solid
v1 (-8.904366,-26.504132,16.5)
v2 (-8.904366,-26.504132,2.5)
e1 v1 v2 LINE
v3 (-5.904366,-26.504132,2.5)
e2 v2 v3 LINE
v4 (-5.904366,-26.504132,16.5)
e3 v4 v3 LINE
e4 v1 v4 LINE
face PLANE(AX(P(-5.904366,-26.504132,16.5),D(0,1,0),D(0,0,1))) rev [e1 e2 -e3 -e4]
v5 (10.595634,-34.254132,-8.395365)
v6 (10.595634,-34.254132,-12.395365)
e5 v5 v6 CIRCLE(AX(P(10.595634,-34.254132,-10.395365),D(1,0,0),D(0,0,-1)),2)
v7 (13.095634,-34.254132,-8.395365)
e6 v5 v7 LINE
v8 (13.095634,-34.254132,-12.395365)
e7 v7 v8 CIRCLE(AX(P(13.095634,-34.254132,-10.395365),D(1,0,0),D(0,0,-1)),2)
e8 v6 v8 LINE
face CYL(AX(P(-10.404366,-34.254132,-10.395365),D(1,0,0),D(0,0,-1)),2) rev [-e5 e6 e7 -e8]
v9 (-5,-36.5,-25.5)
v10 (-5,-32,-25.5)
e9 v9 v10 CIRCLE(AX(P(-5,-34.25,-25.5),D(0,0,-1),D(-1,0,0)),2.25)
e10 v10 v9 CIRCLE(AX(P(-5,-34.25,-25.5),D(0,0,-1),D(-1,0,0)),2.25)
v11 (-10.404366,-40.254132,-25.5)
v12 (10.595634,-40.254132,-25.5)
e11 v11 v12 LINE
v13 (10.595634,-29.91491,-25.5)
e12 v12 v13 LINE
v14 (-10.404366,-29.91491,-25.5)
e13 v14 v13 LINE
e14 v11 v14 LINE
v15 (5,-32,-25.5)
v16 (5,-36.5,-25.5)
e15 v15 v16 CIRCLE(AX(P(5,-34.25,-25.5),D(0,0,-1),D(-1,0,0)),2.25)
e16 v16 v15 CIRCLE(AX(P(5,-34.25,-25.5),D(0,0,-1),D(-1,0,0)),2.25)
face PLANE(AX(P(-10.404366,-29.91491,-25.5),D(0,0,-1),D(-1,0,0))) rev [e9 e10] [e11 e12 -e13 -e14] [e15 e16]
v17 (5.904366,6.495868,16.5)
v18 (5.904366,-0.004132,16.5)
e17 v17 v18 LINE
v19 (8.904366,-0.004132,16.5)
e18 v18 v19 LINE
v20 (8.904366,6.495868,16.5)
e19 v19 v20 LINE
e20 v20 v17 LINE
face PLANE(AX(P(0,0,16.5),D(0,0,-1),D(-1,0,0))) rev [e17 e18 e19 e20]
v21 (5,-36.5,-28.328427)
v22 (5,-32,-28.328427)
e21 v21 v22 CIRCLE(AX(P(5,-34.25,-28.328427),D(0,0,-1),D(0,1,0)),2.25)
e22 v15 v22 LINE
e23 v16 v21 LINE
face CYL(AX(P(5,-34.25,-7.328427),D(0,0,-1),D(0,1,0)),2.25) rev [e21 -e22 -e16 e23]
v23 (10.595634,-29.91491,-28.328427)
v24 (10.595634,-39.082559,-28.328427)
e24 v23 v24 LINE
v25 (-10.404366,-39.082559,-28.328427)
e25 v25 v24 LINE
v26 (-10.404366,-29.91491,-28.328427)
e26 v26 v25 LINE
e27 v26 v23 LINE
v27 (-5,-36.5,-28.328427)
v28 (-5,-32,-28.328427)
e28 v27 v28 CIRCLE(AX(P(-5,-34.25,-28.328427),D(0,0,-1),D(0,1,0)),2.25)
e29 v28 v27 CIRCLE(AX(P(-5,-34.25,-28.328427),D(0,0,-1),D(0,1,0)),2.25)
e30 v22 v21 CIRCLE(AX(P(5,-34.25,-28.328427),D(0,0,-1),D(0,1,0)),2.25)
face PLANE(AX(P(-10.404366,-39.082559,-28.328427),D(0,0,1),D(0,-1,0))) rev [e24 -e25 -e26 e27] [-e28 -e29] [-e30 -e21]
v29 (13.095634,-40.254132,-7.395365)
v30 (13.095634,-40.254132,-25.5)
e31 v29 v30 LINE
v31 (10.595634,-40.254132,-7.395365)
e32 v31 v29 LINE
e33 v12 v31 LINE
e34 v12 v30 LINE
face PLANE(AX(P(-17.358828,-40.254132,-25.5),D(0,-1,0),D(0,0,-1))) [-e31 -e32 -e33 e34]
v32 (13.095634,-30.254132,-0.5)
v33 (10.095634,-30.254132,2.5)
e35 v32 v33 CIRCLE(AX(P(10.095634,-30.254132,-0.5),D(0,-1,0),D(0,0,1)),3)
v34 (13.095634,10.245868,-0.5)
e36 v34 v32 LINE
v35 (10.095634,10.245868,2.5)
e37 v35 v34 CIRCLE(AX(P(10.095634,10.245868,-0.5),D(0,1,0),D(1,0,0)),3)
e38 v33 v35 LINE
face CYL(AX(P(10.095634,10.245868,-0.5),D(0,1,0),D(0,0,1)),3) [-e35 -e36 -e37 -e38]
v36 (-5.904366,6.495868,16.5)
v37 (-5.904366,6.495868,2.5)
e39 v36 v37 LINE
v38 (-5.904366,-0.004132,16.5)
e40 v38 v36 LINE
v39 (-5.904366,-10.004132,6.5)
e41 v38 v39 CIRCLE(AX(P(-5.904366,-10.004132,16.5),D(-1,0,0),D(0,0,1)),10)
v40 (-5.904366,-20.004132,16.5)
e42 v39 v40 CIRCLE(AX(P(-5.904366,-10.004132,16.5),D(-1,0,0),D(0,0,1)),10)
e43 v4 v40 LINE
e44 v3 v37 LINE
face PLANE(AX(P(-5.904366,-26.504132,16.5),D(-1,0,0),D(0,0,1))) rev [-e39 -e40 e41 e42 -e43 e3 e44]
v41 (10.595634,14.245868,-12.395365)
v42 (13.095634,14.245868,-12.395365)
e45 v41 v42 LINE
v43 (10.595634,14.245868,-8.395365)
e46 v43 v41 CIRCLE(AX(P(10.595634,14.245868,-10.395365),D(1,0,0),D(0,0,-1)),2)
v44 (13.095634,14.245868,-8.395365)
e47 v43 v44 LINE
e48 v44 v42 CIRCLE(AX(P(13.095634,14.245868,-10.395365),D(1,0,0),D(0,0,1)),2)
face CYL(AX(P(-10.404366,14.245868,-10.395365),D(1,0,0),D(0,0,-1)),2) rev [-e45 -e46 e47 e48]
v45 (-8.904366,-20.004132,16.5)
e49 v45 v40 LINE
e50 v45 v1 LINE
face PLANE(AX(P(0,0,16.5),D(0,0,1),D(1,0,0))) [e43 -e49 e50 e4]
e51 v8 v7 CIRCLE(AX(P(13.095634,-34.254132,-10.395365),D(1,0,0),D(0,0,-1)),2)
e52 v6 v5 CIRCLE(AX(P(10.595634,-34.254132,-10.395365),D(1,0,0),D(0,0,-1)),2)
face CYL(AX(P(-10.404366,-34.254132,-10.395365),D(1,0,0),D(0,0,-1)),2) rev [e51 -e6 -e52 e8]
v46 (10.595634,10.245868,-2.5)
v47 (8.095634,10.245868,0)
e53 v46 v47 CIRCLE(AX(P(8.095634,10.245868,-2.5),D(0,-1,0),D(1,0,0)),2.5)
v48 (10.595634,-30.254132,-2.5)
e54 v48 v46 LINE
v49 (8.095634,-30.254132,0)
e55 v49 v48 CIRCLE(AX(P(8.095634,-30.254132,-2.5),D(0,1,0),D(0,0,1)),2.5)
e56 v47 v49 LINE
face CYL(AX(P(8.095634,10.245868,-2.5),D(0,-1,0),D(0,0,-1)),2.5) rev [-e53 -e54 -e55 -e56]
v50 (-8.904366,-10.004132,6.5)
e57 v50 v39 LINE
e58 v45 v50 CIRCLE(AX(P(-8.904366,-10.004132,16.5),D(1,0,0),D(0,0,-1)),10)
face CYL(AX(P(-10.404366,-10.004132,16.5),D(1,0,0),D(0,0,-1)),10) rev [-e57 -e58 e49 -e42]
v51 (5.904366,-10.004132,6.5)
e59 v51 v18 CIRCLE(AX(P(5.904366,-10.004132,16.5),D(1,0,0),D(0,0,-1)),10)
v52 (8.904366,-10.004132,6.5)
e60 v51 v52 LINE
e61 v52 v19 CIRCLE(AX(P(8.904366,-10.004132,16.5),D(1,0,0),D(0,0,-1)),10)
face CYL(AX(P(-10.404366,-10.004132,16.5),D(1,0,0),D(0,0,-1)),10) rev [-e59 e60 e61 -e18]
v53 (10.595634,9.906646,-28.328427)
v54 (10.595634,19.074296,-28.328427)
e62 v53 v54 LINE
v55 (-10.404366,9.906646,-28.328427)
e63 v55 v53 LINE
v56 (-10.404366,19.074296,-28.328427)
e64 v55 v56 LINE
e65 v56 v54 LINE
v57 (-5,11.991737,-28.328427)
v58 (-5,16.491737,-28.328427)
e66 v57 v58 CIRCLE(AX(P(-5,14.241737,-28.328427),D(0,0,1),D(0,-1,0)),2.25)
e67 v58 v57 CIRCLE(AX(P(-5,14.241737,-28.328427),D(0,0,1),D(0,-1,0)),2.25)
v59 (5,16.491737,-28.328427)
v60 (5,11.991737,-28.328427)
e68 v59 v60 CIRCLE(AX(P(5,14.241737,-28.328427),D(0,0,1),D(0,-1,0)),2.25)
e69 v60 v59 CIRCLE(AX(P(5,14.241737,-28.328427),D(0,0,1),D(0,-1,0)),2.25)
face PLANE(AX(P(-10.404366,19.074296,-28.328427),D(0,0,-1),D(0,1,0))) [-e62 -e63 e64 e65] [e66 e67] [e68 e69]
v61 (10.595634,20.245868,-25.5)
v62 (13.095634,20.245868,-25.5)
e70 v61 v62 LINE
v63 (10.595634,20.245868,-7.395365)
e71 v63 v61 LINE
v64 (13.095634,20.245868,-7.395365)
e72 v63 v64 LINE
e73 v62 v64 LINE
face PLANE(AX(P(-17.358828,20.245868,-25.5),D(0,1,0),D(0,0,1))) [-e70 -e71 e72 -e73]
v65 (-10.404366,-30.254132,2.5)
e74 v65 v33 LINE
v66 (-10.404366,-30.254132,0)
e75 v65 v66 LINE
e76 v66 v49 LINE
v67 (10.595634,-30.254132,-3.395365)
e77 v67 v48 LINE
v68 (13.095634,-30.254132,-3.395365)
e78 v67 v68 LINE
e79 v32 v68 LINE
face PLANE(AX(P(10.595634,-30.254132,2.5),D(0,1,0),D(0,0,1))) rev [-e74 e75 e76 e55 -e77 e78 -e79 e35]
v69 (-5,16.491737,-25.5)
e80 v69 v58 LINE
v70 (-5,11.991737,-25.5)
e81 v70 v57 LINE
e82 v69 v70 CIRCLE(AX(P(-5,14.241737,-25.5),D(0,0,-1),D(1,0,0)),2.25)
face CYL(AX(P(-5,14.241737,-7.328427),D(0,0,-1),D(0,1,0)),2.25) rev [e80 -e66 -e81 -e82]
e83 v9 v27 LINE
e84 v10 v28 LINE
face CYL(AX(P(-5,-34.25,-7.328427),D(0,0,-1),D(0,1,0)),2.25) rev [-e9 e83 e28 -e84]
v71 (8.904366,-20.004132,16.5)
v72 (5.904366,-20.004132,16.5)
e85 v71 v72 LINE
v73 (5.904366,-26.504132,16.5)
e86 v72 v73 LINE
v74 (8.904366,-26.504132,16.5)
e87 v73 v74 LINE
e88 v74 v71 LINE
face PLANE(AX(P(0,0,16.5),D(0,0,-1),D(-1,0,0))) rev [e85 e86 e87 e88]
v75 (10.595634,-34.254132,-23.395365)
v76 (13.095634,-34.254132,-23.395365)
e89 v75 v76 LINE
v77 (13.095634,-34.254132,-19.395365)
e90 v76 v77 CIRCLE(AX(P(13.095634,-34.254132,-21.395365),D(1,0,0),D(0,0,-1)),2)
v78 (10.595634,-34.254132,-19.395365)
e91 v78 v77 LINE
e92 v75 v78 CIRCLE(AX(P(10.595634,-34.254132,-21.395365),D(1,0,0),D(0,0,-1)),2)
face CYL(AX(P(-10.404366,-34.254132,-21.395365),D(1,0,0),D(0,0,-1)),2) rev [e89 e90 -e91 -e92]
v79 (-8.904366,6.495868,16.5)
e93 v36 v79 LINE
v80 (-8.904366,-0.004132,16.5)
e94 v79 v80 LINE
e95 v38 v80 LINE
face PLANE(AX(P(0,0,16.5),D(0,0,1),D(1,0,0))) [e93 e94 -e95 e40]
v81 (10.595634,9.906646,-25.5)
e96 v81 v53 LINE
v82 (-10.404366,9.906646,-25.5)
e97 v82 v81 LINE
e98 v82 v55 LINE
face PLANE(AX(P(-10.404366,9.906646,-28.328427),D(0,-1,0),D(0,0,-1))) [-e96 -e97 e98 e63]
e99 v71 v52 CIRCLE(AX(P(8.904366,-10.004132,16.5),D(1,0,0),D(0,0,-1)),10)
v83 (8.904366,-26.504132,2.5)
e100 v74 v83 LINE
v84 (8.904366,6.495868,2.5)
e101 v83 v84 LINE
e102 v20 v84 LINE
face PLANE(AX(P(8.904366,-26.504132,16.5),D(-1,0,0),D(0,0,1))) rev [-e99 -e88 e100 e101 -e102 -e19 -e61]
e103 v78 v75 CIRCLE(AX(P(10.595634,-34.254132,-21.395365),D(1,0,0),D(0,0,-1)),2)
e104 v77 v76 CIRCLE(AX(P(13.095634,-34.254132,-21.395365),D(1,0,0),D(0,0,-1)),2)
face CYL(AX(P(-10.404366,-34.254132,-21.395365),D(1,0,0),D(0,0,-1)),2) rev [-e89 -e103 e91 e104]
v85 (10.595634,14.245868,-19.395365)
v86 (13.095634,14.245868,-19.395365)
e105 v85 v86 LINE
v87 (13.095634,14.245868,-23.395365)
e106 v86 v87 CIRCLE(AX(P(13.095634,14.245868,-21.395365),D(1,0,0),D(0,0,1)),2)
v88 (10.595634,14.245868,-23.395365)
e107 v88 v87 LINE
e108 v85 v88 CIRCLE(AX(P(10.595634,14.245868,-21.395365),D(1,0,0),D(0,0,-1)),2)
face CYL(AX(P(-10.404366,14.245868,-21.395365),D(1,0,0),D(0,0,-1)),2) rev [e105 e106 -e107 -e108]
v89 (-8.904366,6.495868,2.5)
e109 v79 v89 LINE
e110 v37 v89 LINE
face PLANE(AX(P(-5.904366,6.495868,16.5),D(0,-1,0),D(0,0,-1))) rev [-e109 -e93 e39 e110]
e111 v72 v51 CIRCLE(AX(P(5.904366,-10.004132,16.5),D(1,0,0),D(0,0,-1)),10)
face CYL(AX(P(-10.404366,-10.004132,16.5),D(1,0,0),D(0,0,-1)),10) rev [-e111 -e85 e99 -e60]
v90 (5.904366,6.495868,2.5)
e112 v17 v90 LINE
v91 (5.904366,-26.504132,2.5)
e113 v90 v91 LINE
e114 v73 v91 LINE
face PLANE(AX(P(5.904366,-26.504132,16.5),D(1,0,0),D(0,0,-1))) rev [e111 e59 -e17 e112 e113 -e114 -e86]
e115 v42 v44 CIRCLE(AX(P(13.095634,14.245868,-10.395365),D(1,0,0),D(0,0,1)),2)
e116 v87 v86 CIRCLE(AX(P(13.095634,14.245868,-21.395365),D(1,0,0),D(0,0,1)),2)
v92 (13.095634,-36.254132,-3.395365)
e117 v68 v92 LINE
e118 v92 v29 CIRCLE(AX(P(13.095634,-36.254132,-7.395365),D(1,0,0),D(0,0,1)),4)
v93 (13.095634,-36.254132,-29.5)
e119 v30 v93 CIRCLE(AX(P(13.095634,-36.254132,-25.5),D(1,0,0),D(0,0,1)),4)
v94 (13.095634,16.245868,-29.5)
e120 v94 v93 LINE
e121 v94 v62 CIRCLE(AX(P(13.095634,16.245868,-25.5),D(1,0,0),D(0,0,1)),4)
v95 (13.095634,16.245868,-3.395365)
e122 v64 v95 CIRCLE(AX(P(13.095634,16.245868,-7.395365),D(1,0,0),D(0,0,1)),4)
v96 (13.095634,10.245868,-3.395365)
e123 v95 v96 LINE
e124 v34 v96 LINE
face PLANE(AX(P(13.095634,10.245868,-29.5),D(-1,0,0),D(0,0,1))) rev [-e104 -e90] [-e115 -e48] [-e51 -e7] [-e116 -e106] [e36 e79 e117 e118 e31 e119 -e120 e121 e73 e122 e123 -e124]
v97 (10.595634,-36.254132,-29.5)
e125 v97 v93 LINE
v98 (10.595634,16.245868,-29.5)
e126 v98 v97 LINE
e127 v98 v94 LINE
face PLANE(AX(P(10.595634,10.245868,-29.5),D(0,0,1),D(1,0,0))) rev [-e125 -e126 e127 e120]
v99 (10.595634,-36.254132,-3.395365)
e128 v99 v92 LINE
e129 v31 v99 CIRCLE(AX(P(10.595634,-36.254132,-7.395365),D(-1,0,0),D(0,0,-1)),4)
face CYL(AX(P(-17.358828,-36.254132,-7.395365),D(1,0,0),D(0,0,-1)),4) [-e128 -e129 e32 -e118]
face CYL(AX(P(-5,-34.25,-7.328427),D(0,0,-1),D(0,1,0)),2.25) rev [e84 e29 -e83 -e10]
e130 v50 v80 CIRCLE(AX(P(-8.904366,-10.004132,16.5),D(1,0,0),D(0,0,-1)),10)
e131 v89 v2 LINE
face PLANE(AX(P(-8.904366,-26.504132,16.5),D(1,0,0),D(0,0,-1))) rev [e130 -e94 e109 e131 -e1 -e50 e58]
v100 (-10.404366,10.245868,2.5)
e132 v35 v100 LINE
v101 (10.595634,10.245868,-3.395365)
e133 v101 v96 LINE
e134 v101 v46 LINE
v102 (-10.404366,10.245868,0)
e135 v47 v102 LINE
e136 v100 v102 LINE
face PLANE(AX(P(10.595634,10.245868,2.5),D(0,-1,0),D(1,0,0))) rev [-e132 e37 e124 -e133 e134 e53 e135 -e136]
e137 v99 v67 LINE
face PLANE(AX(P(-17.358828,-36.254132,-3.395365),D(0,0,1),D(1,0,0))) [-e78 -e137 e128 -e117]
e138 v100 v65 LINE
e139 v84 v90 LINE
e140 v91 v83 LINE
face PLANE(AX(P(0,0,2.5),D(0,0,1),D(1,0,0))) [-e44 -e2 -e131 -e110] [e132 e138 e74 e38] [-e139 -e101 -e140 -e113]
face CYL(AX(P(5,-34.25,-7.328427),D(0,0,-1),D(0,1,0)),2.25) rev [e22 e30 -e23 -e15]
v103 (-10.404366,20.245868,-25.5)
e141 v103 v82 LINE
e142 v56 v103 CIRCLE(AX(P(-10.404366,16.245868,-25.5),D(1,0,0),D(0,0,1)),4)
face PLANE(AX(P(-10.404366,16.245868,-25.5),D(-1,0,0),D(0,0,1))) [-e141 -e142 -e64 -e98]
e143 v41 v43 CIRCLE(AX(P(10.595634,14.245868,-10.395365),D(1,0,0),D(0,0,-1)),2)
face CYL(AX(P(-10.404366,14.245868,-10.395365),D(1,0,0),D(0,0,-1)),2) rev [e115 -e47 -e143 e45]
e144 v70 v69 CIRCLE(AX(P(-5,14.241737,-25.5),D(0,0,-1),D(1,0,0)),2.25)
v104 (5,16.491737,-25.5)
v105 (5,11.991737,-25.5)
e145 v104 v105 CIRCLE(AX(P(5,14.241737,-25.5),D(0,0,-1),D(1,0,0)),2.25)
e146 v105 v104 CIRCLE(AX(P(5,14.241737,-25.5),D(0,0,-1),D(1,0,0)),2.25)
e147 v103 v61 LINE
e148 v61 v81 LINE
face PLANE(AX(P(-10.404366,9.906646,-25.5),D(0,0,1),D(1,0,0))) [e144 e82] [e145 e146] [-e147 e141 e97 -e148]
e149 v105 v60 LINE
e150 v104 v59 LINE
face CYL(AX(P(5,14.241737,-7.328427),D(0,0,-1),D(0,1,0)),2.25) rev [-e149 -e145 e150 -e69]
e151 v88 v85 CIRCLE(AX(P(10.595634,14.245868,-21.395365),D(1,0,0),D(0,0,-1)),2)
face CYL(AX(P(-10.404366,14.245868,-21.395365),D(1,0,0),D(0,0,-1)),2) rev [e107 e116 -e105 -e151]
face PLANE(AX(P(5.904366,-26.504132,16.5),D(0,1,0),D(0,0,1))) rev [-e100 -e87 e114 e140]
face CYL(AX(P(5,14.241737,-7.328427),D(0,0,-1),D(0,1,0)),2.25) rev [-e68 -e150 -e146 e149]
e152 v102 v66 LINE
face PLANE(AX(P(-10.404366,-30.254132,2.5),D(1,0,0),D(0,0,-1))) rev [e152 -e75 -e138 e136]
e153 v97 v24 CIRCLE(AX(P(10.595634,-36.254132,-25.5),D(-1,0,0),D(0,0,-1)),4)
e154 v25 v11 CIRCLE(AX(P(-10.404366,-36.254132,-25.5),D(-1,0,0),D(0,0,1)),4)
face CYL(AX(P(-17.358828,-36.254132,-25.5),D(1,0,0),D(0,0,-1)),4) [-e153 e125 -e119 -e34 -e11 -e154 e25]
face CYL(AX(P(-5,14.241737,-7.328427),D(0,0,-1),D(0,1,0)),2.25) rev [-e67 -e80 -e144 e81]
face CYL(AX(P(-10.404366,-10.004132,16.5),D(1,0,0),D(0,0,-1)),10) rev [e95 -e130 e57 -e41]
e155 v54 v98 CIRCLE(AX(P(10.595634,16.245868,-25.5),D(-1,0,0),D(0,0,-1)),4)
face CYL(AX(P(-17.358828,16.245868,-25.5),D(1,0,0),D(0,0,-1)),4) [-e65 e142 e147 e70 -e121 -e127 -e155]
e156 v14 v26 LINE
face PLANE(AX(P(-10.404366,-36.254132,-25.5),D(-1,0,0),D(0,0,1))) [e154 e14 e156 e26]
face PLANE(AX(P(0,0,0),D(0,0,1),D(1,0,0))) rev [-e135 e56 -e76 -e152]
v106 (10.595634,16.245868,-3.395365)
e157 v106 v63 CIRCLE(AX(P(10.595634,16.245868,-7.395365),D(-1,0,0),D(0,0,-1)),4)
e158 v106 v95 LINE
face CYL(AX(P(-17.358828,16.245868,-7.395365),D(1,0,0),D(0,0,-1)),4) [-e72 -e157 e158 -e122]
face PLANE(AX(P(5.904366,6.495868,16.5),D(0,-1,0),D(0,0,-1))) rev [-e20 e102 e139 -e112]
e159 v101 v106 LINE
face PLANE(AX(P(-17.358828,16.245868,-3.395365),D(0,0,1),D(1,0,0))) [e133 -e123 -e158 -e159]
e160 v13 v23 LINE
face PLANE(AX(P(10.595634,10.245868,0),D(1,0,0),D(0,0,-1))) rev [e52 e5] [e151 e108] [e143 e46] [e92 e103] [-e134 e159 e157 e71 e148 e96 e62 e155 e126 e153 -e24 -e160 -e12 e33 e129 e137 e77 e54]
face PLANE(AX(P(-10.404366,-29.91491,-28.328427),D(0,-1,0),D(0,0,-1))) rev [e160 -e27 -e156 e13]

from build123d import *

# Parameters (mm, degrees)
SKETCH2_W           = 21
SKETCH2_H           = 40.5
BOSS_EXTRUDE1_DEPTH = 2.5
SKETCH3_W           = 3
SKETCH3_H           = 33
BOSS_EXTRUDE2_DEPTH = 14
SKETCH4_R           = 10
CUT_EXTRUDE1_DEPTH  = 40.501767279
BOSS_EXTRUDE3_DEPTH = 20.25
FILLET1_R           = 3
FILLET2_R           = 2.5
BOSS_EXTRUDE4_DEPTH = 2.5
SKETCH7_R           = 2
CUT_EXTRUDE2_DEPTH  = 56.162442887
BOSS_EXTRUDE5_DEPTH = 21
SKETCH10_R          = 2.25
CUT_EXTRUDE3_DEPTH  = 21


with BuildPart() as part:
    # Sketch2 → Boss-Extrude1 (new body)
    with BuildSketch(Plane.XY):
        with Locations((0.095633845, -10.004131531)):
            Rectangle(SKETCH2_W, SKETCH2_H)
    extrude(amount=BOSS_EXTRUDE1_DEPTH)

    # Sketch3 → Boss-Extrude2 (add)
    with BuildSketch(Plane.XY.offset(2.5)):
        with Locations((-7.404366155, -10.004131531)):
            Rectangle(SKETCH3_W, SKETCH3_H)
        with Locations((7.404366155, -10.004131531)):
            Rectangle(SKETCH3_W, SKETCH3_H)
    extrude(amount=BOSS_EXTRUDE2_DEPTH)

    # Sketch4 → Cut-Extrude1 (cut, through all)
    with BuildSketch(Plane(origin=(8.904366155, 0, 0), x_dir=(0, 0, -1), z_dir=(1, 0, 0))):
        with Locations((-16.5, -10.004131531)):
            Circle(SKETCH4_R)
    extrude(amount=-CUT_EXTRUDE1_DEPTH, mode=Mode.SUBTRACT)

    # Sketch5 → Boss-Extrude3 (add, symmetric)
    with BuildSketch(Plane(origin=(0, -10.004131531, 0), x_dir=(1, 0, 0), z_dir=(0, 1, 0))):
        Polygon((10.595633845, 0), (10.595633845, 29.5), (13.095633845, 29.5), (13.095633845, -2.5), (10.595633845, -2.5), align=None)
    extrude(amount=BOSS_EXTRUDE3_DEPTH, both=True)

    # Fillet1
    fillet1_edges = [part.edges().sort_by_distance(p)[0] for p in [
        (13.095633845, -10.004131531, 2.5),
    ]]
    fillet(fillet1_edges, radius=FILLET1_R)

    # Fillet2
    fillet2_edges = [part.edges().sort_by_distance(p)[0] for p in [
        (10.595633845, -10.004131531, 0),
    ]]
    fillet(fillet2_edges, radius=FILLET2_R)

    # Sketch6 → Boss-Extrude4 (add)
    with BuildSketch(Plane(origin=(13.095633845, 0, 0), x_dir=(0, 0, -1), z_dir=(1, 0, 0))):
        with BuildLine():
            Line((29.5, -30.254131531), (29.5, -36.254131531))
            ThreePointArc((29.5, -36.254131531), (28.328427125, -39.082558656), (25.5, -40.254131531))
            Line((25.5, -40.254131531), (7.39536549, -40.254131531))
            ThreePointArc((7.39536549, -40.254131531), (4.566938365, -39.082558656), (3.39536549, -36.254131531))
            Line((3.39536549, -36.254131531), (3.39536549, -30.254131531))
            Line((3.39536549, -30.254131531), (29.5, -30.254131531))
        make_face()
        with BuildLine():
            Line((3.39536549, 10.245868469), (29.5, 10.245868469))
            Line((29.5, 10.245868469), (29.5, 16.245868469))
            ThreePointArc((29.5, 16.245868469), (28.328427125, 19.074295594), (25.5, 20.245868469))
            Line((25.5, 20.245868469), (7.39536549, 20.245868469))
            ThreePointArc((7.39536549, 20.245868469), (4.566938365, 19.074295594), (3.39536549, 16.245868469))
            Line((3.39536549, 16.245868469), (3.39536549, 10.245868469))
        make_face()
    extrude(amount=-BOSS_EXTRUDE4_DEPTH)

    # Sketch7 → Cut-Extrude2 (cut, through all)
    with BuildSketch(Plane(origin=(13.095633845, 0, 0), x_dir=(0, 0, -1), z_dir=(1, 0, 0))):
        with Locations((21.39536549, -34.254131531)):
            Circle(SKETCH7_R)
        with Locations((10.39536549, -34.254131531)):
            Circle(SKETCH7_R)
        with Locations((10.39536549, 14.245868469)):
            Circle(SKETCH7_R)
        with Locations((21.39536549, 14.245868469)):
            Circle(SKETCH7_R)
    extrude(amount=-CUT_EXTRUDE2_DEPTH, mode=Mode.SUBTRACT)

    # Sketch9 → Boss-Extrude5 (add)
    with BuildSketch(Plane.ZY.offset(-10.595633845)):
        with BuildLine():
            Line((-28.328427125, -39.082558656), (-28.328427125, -29.914909502))
            Line((-28.328427125, -29.914909502), (-25.5, -29.914909502))
            Line((-25.5, -29.914909502), (-25.5, -40.254131531))
            ThreePointArc((-25.5, -40.254131531), (-27.030733729, -39.949649661), (-28.328427125, -39.082558656))
        make_face()
    boss_extrude5 = extrude(amount=BOSS_EXTRUDE5_DEPTH)

    # Mirror1: Boss-Extrude5 across plane
    add(boss_extrude5.mirror(Plane.ZX.offset(-10.004131531)))

    # Sketch10 → Cut-Extrude3 (cut)
    with BuildSketch(Plane(origin=(0, 0, -28.328427125), x_dir=(-1, 0, 0), z_dir=(0, 0, -1))):
        with Locations(Location((-5, -34.25, 0), (0, 0, 90))):
            Circle(SKETCH10_R)
        with Locations(Location((5, -34.25, 0), (0, 0, 90))):
            Circle(SKETCH10_R)
    cut_extrude3 = extrude(amount=-CUT_EXTRUDE3_DEPTH, mode=Mode.SUBTRACT)

    # Mirror2: Cut-Extrude3 across plane
    add(cut_extrude3.mirror(Plane.ZX.offset(-10.004131531)), mode=Mode.SUBTRACT)


solid = part.part
